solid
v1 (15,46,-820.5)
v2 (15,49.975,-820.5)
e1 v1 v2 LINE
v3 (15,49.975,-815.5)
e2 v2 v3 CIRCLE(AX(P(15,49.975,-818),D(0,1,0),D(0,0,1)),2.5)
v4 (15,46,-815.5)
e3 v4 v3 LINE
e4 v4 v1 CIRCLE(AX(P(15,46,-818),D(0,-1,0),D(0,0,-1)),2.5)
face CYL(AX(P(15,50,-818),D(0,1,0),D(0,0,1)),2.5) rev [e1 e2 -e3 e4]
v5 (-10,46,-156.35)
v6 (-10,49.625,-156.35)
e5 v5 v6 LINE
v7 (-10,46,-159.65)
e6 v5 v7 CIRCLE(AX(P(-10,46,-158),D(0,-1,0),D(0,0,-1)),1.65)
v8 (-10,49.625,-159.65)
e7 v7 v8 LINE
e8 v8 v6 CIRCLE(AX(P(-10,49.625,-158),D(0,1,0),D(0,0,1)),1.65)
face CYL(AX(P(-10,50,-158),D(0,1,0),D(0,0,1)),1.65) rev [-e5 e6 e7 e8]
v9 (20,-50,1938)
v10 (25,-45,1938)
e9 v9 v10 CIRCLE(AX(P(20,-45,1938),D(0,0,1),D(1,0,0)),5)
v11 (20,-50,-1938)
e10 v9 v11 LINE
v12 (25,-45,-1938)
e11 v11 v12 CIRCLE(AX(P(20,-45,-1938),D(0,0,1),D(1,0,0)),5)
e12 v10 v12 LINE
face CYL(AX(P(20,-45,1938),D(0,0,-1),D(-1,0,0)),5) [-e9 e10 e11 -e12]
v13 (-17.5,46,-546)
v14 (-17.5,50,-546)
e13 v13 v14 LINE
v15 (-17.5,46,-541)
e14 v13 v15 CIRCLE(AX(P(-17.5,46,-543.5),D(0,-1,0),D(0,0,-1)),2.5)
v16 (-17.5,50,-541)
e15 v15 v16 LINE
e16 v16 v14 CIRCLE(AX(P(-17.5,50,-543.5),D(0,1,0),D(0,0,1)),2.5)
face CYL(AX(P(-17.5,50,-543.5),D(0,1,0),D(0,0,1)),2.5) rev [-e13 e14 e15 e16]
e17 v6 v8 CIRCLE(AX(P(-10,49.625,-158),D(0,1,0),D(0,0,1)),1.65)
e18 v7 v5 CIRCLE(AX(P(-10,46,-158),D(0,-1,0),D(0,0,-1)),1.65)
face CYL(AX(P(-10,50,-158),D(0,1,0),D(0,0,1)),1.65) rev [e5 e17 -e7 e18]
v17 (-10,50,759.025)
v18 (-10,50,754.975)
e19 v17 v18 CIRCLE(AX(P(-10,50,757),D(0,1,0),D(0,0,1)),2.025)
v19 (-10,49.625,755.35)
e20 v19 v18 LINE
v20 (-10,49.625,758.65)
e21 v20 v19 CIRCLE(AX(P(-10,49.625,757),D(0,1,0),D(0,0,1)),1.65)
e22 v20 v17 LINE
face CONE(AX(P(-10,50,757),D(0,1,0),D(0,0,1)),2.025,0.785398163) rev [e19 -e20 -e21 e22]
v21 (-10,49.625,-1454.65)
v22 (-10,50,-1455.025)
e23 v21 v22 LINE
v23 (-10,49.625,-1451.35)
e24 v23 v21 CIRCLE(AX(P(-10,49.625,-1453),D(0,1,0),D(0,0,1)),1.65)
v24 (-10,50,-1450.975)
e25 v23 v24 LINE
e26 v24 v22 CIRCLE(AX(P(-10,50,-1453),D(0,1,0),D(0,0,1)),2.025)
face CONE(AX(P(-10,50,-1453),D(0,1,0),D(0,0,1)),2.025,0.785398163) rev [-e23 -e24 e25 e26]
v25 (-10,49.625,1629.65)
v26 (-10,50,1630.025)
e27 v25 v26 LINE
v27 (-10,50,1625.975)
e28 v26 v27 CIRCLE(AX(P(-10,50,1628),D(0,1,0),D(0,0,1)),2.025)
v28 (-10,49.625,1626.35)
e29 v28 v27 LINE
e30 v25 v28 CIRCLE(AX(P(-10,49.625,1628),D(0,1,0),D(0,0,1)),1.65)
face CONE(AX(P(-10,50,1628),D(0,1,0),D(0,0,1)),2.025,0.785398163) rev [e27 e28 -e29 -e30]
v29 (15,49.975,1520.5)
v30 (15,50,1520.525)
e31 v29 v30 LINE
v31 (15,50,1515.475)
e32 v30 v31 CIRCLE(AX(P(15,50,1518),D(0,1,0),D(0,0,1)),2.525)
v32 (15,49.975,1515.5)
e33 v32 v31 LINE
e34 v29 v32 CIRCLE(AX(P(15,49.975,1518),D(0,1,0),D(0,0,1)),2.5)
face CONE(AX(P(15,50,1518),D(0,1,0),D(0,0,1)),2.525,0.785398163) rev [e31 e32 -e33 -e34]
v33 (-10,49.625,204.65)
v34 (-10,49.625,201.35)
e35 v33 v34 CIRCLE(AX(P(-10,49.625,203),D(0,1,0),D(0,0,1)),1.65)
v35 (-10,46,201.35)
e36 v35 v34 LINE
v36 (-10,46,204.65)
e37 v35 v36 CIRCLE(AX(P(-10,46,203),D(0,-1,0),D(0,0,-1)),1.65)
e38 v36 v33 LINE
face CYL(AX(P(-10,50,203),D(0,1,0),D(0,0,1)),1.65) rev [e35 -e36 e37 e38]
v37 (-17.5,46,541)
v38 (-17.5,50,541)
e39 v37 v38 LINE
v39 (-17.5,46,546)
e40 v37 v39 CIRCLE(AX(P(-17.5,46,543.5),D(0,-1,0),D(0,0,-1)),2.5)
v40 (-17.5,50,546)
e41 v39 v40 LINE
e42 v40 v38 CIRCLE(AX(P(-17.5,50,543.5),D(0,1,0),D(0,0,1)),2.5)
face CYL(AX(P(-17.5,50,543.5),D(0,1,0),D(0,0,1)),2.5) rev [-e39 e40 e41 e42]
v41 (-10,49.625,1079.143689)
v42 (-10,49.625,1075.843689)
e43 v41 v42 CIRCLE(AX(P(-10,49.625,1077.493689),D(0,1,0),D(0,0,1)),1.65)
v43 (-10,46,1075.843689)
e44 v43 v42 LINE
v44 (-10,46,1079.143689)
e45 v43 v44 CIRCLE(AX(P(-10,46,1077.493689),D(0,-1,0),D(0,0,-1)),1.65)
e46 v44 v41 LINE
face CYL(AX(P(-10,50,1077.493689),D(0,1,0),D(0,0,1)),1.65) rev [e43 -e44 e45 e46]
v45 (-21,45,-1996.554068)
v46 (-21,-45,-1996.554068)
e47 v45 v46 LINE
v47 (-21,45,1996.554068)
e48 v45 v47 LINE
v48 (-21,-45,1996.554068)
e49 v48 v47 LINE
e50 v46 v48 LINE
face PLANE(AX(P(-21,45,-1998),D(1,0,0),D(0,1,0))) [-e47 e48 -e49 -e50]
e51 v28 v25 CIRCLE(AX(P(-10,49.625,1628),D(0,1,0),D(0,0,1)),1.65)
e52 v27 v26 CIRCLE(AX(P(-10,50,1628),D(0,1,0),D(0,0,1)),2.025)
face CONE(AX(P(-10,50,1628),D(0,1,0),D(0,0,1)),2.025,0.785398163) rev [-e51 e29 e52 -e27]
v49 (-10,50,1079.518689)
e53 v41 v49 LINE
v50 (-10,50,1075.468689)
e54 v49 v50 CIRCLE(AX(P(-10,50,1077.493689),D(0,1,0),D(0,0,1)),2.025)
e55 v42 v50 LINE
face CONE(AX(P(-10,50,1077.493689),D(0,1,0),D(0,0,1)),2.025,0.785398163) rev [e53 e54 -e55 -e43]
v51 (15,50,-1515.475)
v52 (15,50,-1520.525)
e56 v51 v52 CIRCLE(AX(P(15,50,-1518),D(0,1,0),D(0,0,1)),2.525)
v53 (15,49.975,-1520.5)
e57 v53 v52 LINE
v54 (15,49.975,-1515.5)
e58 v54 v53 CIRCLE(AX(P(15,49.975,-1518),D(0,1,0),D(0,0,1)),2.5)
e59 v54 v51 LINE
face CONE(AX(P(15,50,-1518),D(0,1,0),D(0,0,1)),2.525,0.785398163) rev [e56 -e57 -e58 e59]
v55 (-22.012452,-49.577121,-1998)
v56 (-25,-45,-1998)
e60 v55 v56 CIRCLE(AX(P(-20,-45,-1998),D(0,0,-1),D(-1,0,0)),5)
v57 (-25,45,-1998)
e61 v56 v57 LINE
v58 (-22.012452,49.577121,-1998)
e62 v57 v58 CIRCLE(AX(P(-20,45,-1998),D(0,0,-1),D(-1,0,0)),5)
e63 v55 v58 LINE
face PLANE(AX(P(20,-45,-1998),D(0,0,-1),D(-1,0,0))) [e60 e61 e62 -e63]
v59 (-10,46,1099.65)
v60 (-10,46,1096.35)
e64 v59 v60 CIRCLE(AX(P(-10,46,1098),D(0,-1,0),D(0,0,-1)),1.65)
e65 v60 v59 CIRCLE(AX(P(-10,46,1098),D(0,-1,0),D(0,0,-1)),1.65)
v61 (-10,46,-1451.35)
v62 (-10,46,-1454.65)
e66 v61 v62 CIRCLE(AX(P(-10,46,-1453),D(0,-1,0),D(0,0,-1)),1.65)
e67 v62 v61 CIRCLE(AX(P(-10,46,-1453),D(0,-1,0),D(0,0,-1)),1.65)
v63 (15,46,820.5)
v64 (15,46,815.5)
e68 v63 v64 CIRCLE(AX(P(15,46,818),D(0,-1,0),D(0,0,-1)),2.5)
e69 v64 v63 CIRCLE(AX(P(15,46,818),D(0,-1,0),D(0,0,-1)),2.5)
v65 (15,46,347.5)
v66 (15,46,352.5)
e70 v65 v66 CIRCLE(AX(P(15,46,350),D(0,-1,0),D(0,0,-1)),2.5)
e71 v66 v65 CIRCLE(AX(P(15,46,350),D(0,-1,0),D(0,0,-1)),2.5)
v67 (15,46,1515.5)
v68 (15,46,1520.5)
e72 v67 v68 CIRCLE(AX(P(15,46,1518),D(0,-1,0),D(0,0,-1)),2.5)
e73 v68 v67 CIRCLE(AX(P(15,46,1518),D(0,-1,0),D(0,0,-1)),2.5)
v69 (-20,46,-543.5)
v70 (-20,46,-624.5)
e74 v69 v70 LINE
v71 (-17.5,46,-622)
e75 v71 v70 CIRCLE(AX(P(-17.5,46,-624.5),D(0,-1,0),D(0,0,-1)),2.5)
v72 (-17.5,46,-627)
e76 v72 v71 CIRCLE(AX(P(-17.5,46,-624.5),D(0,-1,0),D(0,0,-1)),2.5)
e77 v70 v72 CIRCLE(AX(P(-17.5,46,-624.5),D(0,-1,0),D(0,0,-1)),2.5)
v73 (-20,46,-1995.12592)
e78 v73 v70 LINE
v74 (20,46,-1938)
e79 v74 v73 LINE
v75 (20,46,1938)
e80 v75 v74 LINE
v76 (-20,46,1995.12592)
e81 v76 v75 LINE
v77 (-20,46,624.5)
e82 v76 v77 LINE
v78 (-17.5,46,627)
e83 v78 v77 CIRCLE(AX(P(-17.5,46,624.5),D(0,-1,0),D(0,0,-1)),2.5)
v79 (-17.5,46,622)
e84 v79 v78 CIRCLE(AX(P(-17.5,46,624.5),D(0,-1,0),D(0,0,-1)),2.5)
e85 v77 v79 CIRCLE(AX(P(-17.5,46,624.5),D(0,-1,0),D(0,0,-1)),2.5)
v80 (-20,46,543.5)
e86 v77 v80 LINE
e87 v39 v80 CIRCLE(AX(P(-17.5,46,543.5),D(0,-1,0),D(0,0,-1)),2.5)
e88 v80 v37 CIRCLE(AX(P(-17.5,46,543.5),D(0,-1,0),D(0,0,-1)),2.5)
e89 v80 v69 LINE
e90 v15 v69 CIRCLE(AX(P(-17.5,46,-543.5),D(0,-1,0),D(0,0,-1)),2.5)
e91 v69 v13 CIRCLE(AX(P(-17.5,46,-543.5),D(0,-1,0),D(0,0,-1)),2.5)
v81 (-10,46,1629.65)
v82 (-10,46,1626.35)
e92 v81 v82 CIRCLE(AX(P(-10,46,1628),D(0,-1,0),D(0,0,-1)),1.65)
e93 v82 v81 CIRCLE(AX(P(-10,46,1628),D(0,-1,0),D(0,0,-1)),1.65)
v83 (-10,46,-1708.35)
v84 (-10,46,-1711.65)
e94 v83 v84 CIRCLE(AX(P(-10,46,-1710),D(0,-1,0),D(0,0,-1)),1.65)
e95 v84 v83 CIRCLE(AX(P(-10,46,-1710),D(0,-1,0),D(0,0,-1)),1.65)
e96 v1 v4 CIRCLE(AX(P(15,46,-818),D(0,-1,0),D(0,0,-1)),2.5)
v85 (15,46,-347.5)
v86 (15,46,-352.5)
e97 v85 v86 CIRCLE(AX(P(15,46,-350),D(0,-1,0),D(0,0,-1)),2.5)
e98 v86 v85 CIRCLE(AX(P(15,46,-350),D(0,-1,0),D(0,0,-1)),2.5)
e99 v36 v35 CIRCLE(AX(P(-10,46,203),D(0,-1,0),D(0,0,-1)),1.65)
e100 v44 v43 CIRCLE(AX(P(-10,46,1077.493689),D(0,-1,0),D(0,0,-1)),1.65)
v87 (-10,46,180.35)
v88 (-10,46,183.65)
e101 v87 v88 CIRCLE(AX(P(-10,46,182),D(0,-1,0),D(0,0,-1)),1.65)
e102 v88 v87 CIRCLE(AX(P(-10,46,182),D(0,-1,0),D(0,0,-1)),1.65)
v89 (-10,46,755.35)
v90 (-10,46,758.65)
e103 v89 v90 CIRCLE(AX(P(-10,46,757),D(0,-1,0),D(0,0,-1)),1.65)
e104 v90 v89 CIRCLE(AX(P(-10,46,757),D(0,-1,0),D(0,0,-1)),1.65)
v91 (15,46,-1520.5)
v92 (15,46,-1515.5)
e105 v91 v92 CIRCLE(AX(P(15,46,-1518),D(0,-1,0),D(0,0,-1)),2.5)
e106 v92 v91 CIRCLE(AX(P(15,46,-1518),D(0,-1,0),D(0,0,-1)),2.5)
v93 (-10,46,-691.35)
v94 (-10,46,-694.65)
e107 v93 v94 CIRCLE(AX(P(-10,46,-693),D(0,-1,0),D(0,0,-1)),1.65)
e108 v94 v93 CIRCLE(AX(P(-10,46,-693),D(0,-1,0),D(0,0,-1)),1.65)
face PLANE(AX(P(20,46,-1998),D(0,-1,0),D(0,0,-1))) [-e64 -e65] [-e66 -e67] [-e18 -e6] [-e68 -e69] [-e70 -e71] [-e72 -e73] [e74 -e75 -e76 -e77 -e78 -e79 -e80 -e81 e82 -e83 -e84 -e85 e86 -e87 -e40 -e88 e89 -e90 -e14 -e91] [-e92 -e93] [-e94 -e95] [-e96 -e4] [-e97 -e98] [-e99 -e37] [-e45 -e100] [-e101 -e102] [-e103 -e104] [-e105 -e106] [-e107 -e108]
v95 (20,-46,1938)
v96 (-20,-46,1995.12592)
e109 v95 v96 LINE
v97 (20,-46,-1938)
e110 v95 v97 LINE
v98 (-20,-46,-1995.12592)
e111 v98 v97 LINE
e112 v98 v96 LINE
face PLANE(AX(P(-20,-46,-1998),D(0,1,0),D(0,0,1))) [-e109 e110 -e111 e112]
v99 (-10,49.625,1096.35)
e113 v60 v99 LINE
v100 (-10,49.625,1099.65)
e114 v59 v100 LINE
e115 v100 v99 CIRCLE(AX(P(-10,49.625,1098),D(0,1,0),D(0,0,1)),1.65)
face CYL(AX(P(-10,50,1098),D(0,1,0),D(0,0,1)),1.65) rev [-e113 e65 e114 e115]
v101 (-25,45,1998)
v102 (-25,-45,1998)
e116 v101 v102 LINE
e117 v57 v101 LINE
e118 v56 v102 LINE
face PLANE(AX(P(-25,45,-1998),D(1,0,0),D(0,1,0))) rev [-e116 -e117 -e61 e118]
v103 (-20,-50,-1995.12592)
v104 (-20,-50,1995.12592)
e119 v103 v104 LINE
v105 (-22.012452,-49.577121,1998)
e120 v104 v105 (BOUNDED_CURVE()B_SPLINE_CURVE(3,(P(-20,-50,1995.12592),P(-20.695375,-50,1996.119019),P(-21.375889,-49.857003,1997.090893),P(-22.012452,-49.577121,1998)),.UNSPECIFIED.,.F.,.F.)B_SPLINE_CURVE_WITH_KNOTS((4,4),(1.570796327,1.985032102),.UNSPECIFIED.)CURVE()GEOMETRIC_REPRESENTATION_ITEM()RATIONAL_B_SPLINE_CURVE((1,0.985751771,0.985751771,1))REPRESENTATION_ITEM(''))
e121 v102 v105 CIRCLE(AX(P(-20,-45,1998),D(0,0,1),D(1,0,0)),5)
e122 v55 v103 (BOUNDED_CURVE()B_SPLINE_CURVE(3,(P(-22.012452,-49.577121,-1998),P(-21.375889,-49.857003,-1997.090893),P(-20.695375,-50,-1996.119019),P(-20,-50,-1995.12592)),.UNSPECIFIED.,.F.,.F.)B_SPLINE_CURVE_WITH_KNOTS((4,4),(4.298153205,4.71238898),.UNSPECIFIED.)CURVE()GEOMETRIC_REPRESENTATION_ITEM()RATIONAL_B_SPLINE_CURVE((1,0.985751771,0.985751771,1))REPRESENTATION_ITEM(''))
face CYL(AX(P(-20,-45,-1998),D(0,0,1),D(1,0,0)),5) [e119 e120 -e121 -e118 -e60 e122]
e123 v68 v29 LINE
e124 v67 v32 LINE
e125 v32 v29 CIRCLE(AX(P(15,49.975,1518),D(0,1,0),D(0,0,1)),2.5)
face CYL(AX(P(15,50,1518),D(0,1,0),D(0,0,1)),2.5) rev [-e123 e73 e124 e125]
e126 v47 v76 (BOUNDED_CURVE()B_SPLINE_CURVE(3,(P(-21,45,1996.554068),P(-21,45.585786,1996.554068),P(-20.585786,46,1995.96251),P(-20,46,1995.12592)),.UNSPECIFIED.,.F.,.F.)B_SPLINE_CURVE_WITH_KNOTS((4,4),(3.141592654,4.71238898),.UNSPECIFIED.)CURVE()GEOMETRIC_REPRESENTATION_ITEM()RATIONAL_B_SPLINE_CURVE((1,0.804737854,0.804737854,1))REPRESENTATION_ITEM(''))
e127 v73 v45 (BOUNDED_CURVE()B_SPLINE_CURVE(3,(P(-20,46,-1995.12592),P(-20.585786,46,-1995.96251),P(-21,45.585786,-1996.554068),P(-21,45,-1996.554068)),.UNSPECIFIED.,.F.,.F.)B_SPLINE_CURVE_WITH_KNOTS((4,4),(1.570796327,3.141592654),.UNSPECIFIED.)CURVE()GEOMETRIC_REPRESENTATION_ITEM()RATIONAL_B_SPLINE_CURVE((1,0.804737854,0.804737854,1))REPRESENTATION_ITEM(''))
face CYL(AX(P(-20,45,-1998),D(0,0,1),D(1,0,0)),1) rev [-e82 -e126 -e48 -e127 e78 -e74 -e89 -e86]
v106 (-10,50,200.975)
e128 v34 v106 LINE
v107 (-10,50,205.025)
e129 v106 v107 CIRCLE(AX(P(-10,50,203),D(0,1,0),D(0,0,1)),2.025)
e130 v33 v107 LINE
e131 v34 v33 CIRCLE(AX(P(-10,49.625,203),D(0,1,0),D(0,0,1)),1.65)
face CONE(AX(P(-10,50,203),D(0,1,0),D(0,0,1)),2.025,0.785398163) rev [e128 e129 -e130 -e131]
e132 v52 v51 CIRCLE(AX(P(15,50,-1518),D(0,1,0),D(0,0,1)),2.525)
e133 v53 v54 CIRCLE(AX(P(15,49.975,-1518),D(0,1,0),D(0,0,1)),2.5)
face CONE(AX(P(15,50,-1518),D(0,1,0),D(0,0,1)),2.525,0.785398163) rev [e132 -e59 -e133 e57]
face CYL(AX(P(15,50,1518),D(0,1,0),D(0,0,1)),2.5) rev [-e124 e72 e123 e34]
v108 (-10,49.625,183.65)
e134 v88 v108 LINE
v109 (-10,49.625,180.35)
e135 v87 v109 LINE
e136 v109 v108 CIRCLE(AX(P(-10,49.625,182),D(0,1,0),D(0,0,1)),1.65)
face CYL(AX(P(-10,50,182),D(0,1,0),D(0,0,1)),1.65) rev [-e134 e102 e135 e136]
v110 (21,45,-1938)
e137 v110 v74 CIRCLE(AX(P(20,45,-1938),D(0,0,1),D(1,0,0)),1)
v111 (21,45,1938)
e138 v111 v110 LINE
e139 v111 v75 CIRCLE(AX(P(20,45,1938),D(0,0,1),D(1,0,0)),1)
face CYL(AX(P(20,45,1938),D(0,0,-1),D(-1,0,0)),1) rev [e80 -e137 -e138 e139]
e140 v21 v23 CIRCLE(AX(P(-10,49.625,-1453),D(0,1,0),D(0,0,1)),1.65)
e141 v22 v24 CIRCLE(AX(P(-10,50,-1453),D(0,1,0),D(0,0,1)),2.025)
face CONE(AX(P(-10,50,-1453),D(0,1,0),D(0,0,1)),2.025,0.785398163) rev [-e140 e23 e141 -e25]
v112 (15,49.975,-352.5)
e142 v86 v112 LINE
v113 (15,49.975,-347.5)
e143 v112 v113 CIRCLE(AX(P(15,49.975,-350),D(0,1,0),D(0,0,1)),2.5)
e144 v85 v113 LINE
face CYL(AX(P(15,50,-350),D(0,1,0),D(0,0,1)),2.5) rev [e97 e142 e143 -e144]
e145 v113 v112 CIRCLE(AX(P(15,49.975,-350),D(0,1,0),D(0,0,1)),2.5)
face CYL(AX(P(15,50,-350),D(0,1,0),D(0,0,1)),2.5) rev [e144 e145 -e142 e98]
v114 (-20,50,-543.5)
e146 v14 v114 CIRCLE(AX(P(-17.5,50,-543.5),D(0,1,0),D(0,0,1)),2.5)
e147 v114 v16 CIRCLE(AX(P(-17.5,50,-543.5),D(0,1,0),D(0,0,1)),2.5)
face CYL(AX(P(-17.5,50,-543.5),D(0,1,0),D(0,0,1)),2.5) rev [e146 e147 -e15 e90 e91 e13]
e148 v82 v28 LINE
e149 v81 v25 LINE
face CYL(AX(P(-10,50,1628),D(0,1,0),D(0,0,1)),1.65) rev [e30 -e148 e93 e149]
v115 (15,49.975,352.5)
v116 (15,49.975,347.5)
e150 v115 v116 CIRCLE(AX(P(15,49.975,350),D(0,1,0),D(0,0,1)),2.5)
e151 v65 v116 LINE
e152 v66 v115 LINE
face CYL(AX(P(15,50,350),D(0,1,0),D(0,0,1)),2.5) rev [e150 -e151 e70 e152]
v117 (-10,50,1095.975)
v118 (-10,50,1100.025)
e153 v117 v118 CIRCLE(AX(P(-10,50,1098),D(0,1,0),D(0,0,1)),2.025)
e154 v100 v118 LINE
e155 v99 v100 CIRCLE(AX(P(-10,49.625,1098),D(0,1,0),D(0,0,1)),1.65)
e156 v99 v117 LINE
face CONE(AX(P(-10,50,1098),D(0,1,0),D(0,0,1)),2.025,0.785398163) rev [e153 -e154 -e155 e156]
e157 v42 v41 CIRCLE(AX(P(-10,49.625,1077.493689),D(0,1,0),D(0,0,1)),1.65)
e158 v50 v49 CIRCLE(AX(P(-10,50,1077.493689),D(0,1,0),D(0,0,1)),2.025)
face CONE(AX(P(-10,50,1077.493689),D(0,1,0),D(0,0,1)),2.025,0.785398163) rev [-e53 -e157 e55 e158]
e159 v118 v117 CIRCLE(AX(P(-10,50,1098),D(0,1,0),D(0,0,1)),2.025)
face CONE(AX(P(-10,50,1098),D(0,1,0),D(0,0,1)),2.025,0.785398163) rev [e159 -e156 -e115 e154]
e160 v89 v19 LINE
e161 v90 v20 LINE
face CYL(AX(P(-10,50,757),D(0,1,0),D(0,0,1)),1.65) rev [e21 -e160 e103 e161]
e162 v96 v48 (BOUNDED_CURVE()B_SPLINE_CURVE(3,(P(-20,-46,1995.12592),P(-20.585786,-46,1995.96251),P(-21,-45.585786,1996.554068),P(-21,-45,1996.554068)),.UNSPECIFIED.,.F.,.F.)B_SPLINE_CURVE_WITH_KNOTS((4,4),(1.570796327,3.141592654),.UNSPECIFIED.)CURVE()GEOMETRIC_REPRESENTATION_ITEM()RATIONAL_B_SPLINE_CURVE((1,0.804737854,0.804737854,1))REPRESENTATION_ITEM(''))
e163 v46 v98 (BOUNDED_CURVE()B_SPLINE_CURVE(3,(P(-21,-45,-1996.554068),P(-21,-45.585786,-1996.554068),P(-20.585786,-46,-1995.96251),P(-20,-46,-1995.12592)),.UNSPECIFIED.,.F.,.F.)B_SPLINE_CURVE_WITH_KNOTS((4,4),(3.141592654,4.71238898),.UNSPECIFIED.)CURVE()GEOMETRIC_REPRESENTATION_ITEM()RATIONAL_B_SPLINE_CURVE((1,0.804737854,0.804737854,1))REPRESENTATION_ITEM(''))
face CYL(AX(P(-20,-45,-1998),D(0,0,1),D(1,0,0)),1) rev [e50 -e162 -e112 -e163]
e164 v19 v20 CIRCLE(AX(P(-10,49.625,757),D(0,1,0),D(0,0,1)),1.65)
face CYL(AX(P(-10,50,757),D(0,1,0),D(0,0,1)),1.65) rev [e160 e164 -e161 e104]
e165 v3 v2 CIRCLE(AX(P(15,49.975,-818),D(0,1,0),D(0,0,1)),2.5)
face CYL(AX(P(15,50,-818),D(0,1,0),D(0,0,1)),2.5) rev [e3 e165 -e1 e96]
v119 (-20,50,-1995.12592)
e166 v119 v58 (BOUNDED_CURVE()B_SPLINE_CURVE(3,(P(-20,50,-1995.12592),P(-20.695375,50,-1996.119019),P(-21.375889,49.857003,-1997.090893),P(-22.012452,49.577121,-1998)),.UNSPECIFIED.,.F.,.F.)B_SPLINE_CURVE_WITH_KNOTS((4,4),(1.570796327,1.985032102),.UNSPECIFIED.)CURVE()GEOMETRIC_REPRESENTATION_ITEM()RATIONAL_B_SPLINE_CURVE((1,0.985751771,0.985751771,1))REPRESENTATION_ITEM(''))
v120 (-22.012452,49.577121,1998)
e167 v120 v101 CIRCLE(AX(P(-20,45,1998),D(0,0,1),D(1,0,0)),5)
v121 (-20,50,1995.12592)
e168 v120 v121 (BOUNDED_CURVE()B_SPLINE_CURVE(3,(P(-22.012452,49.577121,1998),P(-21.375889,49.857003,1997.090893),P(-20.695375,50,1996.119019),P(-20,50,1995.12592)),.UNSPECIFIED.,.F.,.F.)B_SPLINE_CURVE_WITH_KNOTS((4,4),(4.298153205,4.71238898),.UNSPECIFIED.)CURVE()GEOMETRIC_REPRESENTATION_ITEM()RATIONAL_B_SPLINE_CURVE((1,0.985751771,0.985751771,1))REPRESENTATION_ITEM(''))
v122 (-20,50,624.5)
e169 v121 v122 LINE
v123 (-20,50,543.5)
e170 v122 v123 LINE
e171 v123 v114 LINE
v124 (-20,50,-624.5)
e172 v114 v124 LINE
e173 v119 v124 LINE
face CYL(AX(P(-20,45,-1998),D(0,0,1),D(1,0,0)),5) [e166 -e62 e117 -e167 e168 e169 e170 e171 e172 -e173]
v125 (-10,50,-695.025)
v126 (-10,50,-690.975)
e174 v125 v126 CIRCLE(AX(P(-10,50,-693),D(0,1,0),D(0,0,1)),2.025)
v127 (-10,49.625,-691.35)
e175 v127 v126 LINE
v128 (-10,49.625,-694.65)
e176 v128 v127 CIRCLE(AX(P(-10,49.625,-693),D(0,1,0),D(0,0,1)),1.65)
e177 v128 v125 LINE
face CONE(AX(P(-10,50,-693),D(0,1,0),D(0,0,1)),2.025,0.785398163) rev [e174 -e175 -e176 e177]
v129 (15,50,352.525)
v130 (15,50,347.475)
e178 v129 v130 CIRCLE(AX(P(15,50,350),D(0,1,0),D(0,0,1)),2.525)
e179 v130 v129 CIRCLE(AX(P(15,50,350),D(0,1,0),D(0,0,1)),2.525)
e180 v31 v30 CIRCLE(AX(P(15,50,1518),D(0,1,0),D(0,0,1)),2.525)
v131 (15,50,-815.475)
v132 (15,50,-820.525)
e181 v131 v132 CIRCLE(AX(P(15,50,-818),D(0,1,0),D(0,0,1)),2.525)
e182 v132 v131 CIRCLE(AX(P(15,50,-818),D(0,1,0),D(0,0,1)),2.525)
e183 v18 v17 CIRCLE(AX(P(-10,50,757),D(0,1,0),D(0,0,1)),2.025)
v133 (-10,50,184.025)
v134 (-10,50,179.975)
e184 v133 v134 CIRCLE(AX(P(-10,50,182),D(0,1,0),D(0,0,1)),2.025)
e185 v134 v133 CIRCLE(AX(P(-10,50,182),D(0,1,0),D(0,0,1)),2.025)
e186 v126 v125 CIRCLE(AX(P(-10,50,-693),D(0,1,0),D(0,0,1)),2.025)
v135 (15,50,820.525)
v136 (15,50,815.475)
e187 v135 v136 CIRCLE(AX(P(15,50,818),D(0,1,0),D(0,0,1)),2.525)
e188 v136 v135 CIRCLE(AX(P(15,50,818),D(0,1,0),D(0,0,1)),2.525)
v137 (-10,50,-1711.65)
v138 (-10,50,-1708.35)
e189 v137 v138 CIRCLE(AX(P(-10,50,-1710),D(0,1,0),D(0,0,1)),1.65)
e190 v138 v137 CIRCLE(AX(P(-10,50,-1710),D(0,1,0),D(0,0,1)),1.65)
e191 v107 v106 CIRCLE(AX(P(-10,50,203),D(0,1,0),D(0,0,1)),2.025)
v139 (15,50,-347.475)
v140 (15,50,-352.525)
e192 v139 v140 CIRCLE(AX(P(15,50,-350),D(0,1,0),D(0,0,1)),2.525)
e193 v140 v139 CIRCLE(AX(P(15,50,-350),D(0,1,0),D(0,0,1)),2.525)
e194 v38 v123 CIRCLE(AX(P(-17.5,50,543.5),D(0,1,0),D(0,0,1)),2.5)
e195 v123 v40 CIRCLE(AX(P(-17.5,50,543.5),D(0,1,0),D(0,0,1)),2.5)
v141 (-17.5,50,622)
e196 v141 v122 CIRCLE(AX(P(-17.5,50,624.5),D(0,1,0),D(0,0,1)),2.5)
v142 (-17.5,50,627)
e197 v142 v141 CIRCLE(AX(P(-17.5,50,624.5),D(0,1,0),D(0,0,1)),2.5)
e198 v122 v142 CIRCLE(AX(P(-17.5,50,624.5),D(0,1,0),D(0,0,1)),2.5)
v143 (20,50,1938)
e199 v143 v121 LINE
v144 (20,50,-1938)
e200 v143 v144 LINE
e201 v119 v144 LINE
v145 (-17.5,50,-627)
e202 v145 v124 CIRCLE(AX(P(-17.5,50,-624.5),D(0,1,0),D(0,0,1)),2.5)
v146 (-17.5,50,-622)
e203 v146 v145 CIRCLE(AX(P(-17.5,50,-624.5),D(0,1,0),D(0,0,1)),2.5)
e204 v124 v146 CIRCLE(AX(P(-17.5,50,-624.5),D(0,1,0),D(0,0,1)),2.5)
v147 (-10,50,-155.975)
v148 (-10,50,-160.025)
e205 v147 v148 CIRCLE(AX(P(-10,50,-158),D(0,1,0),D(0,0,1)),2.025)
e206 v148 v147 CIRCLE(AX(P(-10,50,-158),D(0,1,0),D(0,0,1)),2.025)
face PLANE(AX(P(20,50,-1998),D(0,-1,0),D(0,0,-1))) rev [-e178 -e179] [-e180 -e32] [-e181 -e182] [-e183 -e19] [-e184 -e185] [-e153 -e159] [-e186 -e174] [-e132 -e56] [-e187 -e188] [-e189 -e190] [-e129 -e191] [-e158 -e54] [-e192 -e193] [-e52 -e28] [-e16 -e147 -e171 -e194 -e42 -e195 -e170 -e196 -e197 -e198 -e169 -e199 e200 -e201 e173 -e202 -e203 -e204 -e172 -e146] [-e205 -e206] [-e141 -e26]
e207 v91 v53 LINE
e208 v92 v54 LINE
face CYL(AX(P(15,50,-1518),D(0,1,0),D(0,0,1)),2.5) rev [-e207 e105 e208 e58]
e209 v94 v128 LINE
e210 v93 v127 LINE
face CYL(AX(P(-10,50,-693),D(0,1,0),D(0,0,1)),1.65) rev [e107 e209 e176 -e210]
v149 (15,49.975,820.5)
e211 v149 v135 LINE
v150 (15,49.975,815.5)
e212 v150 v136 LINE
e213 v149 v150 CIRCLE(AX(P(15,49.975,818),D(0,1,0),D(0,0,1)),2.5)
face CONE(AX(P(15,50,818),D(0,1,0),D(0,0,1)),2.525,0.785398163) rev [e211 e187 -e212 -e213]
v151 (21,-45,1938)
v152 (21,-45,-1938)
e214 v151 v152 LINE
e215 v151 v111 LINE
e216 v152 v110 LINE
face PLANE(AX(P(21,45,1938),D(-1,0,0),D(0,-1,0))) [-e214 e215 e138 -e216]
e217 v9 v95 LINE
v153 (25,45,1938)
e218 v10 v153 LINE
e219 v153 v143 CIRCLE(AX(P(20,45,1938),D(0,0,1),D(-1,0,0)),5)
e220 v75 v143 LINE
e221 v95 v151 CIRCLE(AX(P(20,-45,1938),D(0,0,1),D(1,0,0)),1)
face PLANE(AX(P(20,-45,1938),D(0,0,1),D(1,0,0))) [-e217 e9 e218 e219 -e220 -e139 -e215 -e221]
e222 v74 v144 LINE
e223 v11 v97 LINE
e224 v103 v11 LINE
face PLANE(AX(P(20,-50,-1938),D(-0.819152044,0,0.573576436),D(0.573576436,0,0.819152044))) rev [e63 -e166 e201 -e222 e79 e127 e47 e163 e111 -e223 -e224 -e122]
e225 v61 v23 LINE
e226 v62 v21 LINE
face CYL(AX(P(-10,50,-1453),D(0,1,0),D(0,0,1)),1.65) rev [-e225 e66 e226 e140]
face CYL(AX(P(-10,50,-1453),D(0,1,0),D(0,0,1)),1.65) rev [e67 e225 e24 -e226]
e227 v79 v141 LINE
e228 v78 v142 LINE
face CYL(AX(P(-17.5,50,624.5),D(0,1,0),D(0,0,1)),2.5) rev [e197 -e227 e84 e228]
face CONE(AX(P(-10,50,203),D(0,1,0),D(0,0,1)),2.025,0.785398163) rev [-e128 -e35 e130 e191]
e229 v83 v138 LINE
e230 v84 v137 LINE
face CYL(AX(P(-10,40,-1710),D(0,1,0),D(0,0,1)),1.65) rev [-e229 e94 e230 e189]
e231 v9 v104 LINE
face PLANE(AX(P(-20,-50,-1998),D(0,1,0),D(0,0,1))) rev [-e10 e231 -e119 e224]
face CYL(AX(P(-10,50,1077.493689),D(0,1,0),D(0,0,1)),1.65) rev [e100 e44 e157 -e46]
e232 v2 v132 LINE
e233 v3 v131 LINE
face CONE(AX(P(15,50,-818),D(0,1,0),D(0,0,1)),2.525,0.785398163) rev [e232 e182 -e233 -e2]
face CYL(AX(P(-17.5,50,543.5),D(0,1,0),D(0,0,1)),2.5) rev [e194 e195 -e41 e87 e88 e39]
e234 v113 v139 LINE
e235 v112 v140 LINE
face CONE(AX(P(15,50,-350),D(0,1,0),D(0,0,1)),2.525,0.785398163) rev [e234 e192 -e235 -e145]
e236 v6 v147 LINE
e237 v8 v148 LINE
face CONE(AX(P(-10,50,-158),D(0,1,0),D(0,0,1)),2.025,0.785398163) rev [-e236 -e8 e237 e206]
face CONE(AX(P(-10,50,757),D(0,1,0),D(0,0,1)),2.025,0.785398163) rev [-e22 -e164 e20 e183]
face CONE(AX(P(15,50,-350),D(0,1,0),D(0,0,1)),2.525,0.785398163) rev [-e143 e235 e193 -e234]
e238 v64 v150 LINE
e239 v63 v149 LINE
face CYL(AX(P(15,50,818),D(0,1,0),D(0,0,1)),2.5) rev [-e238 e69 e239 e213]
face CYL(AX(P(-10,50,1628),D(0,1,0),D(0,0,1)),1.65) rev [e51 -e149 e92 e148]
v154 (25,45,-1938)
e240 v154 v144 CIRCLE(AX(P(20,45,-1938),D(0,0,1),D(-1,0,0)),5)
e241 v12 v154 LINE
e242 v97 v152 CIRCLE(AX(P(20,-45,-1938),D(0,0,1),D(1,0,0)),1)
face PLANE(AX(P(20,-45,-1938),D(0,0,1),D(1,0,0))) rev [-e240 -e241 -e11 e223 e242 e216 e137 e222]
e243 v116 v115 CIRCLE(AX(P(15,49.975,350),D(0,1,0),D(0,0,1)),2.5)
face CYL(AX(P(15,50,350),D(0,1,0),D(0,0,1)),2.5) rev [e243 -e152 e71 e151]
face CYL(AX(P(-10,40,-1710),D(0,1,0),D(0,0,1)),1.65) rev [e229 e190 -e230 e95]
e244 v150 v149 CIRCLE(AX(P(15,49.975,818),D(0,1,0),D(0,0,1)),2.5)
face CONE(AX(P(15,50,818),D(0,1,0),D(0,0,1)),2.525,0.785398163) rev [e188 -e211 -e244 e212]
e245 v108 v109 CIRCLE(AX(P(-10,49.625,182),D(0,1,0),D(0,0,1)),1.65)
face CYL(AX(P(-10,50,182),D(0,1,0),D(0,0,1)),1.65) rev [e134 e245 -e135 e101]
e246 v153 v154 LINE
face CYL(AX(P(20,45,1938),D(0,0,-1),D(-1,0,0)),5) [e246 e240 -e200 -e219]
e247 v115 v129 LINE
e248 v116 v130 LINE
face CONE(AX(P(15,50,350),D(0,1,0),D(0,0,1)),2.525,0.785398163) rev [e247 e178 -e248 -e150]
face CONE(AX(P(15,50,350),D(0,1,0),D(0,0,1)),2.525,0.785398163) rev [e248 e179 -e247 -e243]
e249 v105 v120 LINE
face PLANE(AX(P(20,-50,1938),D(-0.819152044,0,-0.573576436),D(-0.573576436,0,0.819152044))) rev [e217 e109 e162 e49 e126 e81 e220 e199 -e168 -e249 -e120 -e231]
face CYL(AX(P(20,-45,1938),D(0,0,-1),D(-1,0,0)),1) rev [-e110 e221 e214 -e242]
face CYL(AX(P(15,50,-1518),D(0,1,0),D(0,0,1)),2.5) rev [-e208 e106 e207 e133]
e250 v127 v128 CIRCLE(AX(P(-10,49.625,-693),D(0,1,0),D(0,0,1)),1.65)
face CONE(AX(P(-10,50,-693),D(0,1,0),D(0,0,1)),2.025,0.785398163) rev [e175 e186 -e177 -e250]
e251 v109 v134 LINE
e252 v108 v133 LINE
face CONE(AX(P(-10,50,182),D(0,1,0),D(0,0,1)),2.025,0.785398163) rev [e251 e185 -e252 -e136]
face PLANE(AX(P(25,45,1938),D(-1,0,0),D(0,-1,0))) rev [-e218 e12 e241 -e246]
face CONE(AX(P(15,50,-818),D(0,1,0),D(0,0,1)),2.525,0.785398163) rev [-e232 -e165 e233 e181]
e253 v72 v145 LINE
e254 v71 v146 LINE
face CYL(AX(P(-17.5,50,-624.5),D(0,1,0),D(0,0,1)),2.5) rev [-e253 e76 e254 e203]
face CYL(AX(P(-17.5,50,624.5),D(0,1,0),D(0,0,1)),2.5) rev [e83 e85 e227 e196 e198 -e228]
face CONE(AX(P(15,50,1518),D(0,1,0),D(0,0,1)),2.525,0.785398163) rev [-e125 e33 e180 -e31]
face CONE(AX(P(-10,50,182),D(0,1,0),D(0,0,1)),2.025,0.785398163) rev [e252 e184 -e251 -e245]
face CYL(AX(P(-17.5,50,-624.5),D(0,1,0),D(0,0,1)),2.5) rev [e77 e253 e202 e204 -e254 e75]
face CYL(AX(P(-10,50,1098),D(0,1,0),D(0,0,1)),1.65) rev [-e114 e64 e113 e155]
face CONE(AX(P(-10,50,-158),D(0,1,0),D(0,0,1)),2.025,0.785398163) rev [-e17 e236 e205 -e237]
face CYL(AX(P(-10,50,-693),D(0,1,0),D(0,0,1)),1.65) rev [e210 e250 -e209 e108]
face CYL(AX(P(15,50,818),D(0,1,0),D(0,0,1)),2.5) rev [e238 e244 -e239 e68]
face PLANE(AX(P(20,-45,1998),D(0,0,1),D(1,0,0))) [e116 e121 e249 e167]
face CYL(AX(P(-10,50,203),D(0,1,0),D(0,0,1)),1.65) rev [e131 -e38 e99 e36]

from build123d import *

# Parameters (mm, degrees)
EXTRUDE_1_DEPTH             = 1938
EXTRUDE_1_2_DEPTH           = 60
CUT_EXTRUDE_2_DEPTH         = 2001.657142041
EXTRUDE_2_DEPTH             = 60
CUT_EXTRUDE_3_DEPTH         = 2001.657142041
HOLE_WIZARD_M6_1_AT_2_COUNT = 2
HOLE_WIZARD_M6_1_AT_2_PITCH = 81
HOLE_WIZARD_M6_1_AT_3_COUNT = 2
HOLE_WIZARD_M6_1_AT_3_PITCH = 1168
HOLE_WIZARD_M6_1_AT_4_COUNT = 2
HOLE_WIZARD_M6_1_AT_4_PITCH = 1249
MM_1_AT_2_COUNT             = 2
MM_1_AT_2_PITCH             = 700
PATTERN_LINEAR_1_COUNT      = 3
PATTERN_LINEAR_1_PITCH      = 1168
HOLE_WIZARD_M4_1_AT_2_COUNT = 2
HOLE_WIZARD_M4_1_AT_2_PITCH = 530
HOLE_WIZARD_M4_1_AT_3_COUNT = 2
HOLE_WIZARD_M4_1_AT_3_PITCH = 550.506310809
HOLE_WIZARD_M4_1_AT_4_COUNT = 2
HOLE_WIZARD_M4_1_AT_4_PITCH = 871
HOLE_WIZARD_M4_1_AT_5_COUNT = 2
HOLE_WIZARD_M4_1_AT_5_PITCH = 1425
HOLE_WIZARD_M4_1_AT_6_COUNT = 2
HOLE_WIZARD_M4_1_AT_6_PITCH = 1446
HOLE_WIZARD_M4_1_AT_7_COUNT = 2
HOLE_WIZARD_M4_1_AT_7_PITCH = 1786
HOLE_WIZARD_M4_1_AT_8_COUNT = 2
HOLE_WIZARD_M4_1_AT_8_PITCH = 2321
SKETCH_20_R                 = 1.65
CUT_EXTRUDE_4_DEPTH         = 10


with BuildPart() as part:
    # 草图1 → Extrude 1 (new, symmetric)
    with BuildSketch(Plane.XY):
        with BuildLine():
            Line((-20, 50), (20, 50))
            ThreePointArc((20, 50), (23.535533906, 48.535533906), (25, 45))
            Line((25, 45), (25, -45))
            ThreePointArc((25, -45), (23.535533906, -48.535533906), (20, -50))
            Line((20, -50), (-20, -50))
            ThreePointArc((-20, -50), (-23.535533906, -48.535533906), (-25, -45))
            Line((-25, -45), (-25, 45))
            ThreePointArc((-25, 45), (-23.535533906, 48.535533906), (-20, 50))
        make_face()
        with BuildLine():
            Line((-20, 46), (20, 46))
            ThreePointArc((20, 46), (20.707106781, 45.707106781), (21, 45))
            Line((21, 45), (21, -45))
            ThreePointArc((21, -45), (20.707106781, -45.707106781), (20, -46))
            Line((20, -46), (-20, -46))
            ThreePointArc((-20, -46), (-20.707106781, -45.707106781), (-21, -45))
            Line((-21, -45), (-21, 45))
            ThreePointArc((-21, 45), (-20.707106781, 45.707106781), (-20, 46))
        make_face(mode=Mode.SUBTRACT)
    extrude(amount=EXTRUDE_1_DEPTH, both=True)

    # 草图12 → M6 螺纹孔1 (revolve, cut)
    with BuildSketch(Plane(origin=(-17.5, 50, -624.5), x_dir=(0, 0, 1), z_dir=(1, 0, 0))):
        Polygon((0, 0), (0, 16.502151548), (2.5, 15), (2.5, 0), align=None)
    hole_wizard_m6_1 = revolve(axis=Axis((-17.5, 56.35, -624.5), (0, -1, 0)), mode=Mode.SUBTRACT)

    # M6 螺纹孔1 at 2: M6 螺纹孔1 ×2
    with Locations(*[(0, 0, i * HOLE_WIZARD_M6_1_AT_2_PITCH) for i in range(1, HOLE_WIZARD_M6_1_AT_2_COUNT)]):
        add(hole_wizard_m6_1, mode=Mode.SUBTRACT)

    # M6 螺纹孔1 at 3: M6 螺纹孔1 ×2
    with Locations(*[(0, 0, i * HOLE_WIZARD_M6_1_AT_3_PITCH) for i in range(1, HOLE_WIZARD_M6_1_AT_3_COUNT)]):
        add(hole_wizard_m6_1, mode=Mode.SUBTRACT)

    # M6 螺纹孔1 at 4: M6 螺纹孔1 ×2
    with Locations(*[(0, 0, i * HOLE_WIZARD_M6_1_AT_4_PITCH) for i in range(1, HOLE_WIZARD_M6_1_AT_4_COUNT)]):
        add(hole_wizard_m6_1, mode=Mode.SUBTRACT)

    # 草图14 → 大小mm 暗销孔1 (revolve, cut)
    with BuildSketch(Plane(origin=(15, 50, -818), x_dir=(0, 0, 1), z_dir=(1, 0, 0))):
        Polygon((0, 0), (0, 10.002151548), (2.5, 8.5), (2.5, 0.025), (2.525, 0), align=None)
    mm_1 = revolve(axis=Axis((15, 56.35, -818), (0, -1, 0)), mode=Mode.SUBTRACT)

    # 大小mm 暗销孔1 at 2: 大小mm 暗销孔1 ×2
    with Locations(*[(0, 0, -i * MM_1_AT_2_PITCH) for i in range(1, MM_1_AT_2_COUNT)]):
        add(mm_1, mode=Mode.SUBTRACT)

    # 阵列(线性)1: 大小mm 暗销孔1 ×3
    with Locations(*[(0, 0, i * PATTERN_LINEAR_1_PITCH) for i in range(1, PATTERN_LINEAR_1_COUNT)]):
        add(mm_1, mode=Mode.SUBTRACT)

    # 阵列(线性)1 copy 1 sketch → 阵列(线性)1 copy 1 (revolve, cut)
    with BuildSketch(Plane(origin=(15, 50, -350), x_dir=(0, 0, 1), z_dir=(1, 0, 0))):
        Polygon((0, 0), (0, 10.002151548), (2.5, 8.5), (2.5, 0.025), (2.525, 0), align=None)
    revolve(axis=Axis((15, 56.35, -350), (0, -1, 0)), mode=Mode.SUBTRACT)

    # 阵列(线性)1 copy 2 sketch → 阵列(线性)1 copy 2 (revolve, cut)
    with BuildSketch(Plane(origin=(15, 50, 818), x_dir=(0, 0, 1), z_dir=(1, 0, 0))):
        Polygon((0, 0), (0, 10.002151548), (2.5, 8.5), (2.5, 0.025), (2.525, 0), align=None)
    revolve(axis=Axis((15, 56.35, 818), (0, -1, 0)), mode=Mode.SUBTRACT)

    # 草图17 → M4 螺纹孔1 (revolve, cut)
    with BuildSketch(Plane(origin=(-10, 50, 1628), x_dir=(0, 0, 1), z_dir=(1, 0, 0))):
        Polygon((0, 0), (0, 11.091420021), (1.65, 10.1), (1.65, 0.375), (2.025, 0), align=None)
    hole_wizard_m4_1 = revolve(axis=Axis((-10, 56.35, 1628), (0, -1, 0)), mode=Mode.SUBTRACT)

    # M4 螺纹孔1 at 2: M4 螺纹孔1 ×2
    with Locations(*[(0, 0, -i * HOLE_WIZARD_M4_1_AT_2_PITCH) for i in range(1, HOLE_WIZARD_M4_1_AT_2_COUNT)]):
        add(hole_wizard_m4_1, mode=Mode.SUBTRACT)

    # M4 螺纹孔1 at 3: M4 螺纹孔1 ×2
    with Locations(*[(0, 0, -i * HOLE_WIZARD_M4_1_AT_3_PITCH) for i in range(1, HOLE_WIZARD_M4_1_AT_3_COUNT)]):
        add(hole_wizard_m4_1, mode=Mode.SUBTRACT)

    # M4 螺纹孔1 at 4: M4 螺纹孔1 ×2
    with Locations(*[(0, 0, -i * HOLE_WIZARD_M4_1_AT_4_PITCH) for i in range(1, HOLE_WIZARD_M4_1_AT_4_COUNT)]):
        add(hole_wizard_m4_1, mode=Mode.SUBTRACT)

    # M4 螺纹孔1 at 5: M4 螺纹孔1 ×2
    with Locations(*[(0, 0, -i * HOLE_WIZARD_M4_1_AT_5_PITCH) for i in range(1, HOLE_WIZARD_M4_1_AT_5_COUNT)]):
        add(hole_wizard_m4_1, mode=Mode.SUBTRACT)

    # M4 螺纹孔1 at 6: M4 螺纹孔1 ×2
    with Locations(*[(0, 0, -i * HOLE_WIZARD_M4_1_AT_6_PITCH) for i in range(1, HOLE_WIZARD_M4_1_AT_6_COUNT)]):
        add(hole_wizard_m4_1, mode=Mode.SUBTRACT)

    # M4 螺纹孔1 at 7: M4 螺纹孔1 ×2
    with Locations(*[(0, 0, -i * HOLE_WIZARD_M4_1_AT_7_PITCH) for i in range(1, HOLE_WIZARD_M4_1_AT_7_COUNT)]):
        add(hole_wizard_m4_1, mode=Mode.SUBTRACT)

    # M4 螺纹孔1 at 8: M4 螺纹孔1 ×2
    with Locations(*[(0, 0, -i * HOLE_WIZARD_M4_1_AT_8_PITCH) for i in range(1, HOLE_WIZARD_M4_1_AT_8_COUNT)]):
        add(hole_wizard_m4_1, mode=Mode.SUBTRACT)

    # 草图19 → M4 螺纹孔2 (revolve, cut)
    with BuildSketch(Plane(origin=(-10, 50, -1453), x_dir=(0, 0, 1), z_dir=(1, 0, 0))):
        Polygon((0, 0), (0, 11.091420021), (1.65, 10.1), (1.65, 0.375), (2.025, 0), align=None)
    revolve(axis=Axis((-10, 56.35, -1453), (0, -1, 0)), mode=Mode.SUBTRACT)


with BuildPart() as body_2:
    # 草图7 → Extrude 1 2 (new body)
    with BuildSketch(Plane.XY.offset(1938)):
        with BuildLine():
            Line((25, -45), (25, 45))
            ThreePointArc((25, 45), (23.535533906, 48.535533906), (20, 50))
            Line((20, 50), (-20, 50))
            ThreePointArc((-20, 50), (-23.535533906, 48.535533906), (-25, 45))
            Line((-25, 45), (-25, -45))
            ThreePointArc((-25, -45), (-23.535533906, -48.535533906), (-20, -50))
            Line((-20, -50), (20, -50))
            ThreePointArc((20, -50), (23.535533906, -48.535533906), (25, -45))
        make_face()
        with BuildLine():
            Line((21, -45), (21, 45))
            ThreePointArc((21, 45), (20.707106781, 45.707106781), (20, 46))
            Line((20, 46), (-20, 46))
            ThreePointArc((-20, 46), (-20.707106781, 45.707106781), (-21, 45))
            Line((-21, 45), (-21, -45))
            ThreePointArc((-21, -45), (-20.707106781, -45.707106781), (-20, -46))
            Line((-20, -46), (20, -46))
            ThreePointArc((20, -46), (20.707106781, -45.707106781), (21, -45))
        make_face(mode=Mode.SUBTRACT)
    extrude(amount=EXTRUDE_1_2_DEPTH)

    # 草图8 → 切除-拉伸2 (cut, through all)
    with BuildSketch(Plane(origin=(0, 50, 0), x_dir=(1, 0, 0), z_dir=(0, 1, 0))):
        Polygon((20, -1938), (-22.012452293, -1998), (31.913764891, -1998), (31.913764891, -1938), align=None)
    extrude(amount=-CUT_EXTRUDE_2_DEPTH, mode=Mode.SUBTRACT)


with BuildPart() as body_3:
    # 草图9 → 凸台-拉伸2 (new body)
    with BuildSketch(Plane(origin=(0, 0, -1938), x_dir=(-1, 0, 0), z_dir=(0, 0, -1))):
        with BuildLine():
            Line((20, -50), (-20, -50))
            ThreePointArc((-20, -50), (-23.535533906, -48.535533906), (-25, -45))
            Line((-25, -45), (-25, 45))
            ThreePointArc((-25, 45), (-23.535533906, 48.535533906), (-20, 50))
            Line((-20, 50), (20, 50))
            ThreePointArc((20, 50), (23.535533906, 48.535533906), (25, 45))
            Line((25, 45), (25, -45))
            ThreePointArc((25, -45), (23.535533906, -48.535533906), (20, -50))
        make_face()
        with BuildLine():
            Line((-20, 46), (20, 46))
            ThreePointArc((20, 46), (20.707106781, 45.707106781), (21, 45))
            Line((21, 45), (21, -45))
            ThreePointArc((21, -45), (20.707106781, -45.707106781), (20, -46))
            Line((20, -46), (-20, -46))
            ThreePointArc((-20, -46), (-20.707106781, -45.707106781), (-21, -45))
            Line((-21, -45), (-21, 45))
            ThreePointArc((-21, 45), (-20.707106781, 45.707106781), (-20, 46))
        make_face(mode=Mode.SUBTRACT)
    extrude(amount=EXTRUDE_2_DEPTH)

    # 草图10 → 切除-拉伸3 (cut, through all)
    with BuildSketch(Plane(origin=(0, 50, 0), x_dir=(1, 0, 0), z_dir=(0, 1, 0))):
        Polygon((20, 1938), (-22.012452293, 1998), (25, 1998), (25, 1938), align=None)
    extrude(amount=-CUT_EXTRUDE_3_DEPTH, mode=Mode.SUBTRACT)

    # Combine 1: union part
    add(part.part)

    # Combine 2: union body 2
    add(body_2.part)

    # 草图20 → 切除-拉伸4 (cut)
    with BuildSketch(Plane(origin=(0, 50, 0), x_dir=(1, 0, 0), z_dir=(0, 1, 0))):
        with Locations(Location((-10, 1710, 0), (0, 0, 270))):
            Circle(SKETCH_20_R)
    extrude(amount=-CUT_EXTRUDE_4_DEPTH, mode=Mode.SUBTRACT)


solid = body_3.part
